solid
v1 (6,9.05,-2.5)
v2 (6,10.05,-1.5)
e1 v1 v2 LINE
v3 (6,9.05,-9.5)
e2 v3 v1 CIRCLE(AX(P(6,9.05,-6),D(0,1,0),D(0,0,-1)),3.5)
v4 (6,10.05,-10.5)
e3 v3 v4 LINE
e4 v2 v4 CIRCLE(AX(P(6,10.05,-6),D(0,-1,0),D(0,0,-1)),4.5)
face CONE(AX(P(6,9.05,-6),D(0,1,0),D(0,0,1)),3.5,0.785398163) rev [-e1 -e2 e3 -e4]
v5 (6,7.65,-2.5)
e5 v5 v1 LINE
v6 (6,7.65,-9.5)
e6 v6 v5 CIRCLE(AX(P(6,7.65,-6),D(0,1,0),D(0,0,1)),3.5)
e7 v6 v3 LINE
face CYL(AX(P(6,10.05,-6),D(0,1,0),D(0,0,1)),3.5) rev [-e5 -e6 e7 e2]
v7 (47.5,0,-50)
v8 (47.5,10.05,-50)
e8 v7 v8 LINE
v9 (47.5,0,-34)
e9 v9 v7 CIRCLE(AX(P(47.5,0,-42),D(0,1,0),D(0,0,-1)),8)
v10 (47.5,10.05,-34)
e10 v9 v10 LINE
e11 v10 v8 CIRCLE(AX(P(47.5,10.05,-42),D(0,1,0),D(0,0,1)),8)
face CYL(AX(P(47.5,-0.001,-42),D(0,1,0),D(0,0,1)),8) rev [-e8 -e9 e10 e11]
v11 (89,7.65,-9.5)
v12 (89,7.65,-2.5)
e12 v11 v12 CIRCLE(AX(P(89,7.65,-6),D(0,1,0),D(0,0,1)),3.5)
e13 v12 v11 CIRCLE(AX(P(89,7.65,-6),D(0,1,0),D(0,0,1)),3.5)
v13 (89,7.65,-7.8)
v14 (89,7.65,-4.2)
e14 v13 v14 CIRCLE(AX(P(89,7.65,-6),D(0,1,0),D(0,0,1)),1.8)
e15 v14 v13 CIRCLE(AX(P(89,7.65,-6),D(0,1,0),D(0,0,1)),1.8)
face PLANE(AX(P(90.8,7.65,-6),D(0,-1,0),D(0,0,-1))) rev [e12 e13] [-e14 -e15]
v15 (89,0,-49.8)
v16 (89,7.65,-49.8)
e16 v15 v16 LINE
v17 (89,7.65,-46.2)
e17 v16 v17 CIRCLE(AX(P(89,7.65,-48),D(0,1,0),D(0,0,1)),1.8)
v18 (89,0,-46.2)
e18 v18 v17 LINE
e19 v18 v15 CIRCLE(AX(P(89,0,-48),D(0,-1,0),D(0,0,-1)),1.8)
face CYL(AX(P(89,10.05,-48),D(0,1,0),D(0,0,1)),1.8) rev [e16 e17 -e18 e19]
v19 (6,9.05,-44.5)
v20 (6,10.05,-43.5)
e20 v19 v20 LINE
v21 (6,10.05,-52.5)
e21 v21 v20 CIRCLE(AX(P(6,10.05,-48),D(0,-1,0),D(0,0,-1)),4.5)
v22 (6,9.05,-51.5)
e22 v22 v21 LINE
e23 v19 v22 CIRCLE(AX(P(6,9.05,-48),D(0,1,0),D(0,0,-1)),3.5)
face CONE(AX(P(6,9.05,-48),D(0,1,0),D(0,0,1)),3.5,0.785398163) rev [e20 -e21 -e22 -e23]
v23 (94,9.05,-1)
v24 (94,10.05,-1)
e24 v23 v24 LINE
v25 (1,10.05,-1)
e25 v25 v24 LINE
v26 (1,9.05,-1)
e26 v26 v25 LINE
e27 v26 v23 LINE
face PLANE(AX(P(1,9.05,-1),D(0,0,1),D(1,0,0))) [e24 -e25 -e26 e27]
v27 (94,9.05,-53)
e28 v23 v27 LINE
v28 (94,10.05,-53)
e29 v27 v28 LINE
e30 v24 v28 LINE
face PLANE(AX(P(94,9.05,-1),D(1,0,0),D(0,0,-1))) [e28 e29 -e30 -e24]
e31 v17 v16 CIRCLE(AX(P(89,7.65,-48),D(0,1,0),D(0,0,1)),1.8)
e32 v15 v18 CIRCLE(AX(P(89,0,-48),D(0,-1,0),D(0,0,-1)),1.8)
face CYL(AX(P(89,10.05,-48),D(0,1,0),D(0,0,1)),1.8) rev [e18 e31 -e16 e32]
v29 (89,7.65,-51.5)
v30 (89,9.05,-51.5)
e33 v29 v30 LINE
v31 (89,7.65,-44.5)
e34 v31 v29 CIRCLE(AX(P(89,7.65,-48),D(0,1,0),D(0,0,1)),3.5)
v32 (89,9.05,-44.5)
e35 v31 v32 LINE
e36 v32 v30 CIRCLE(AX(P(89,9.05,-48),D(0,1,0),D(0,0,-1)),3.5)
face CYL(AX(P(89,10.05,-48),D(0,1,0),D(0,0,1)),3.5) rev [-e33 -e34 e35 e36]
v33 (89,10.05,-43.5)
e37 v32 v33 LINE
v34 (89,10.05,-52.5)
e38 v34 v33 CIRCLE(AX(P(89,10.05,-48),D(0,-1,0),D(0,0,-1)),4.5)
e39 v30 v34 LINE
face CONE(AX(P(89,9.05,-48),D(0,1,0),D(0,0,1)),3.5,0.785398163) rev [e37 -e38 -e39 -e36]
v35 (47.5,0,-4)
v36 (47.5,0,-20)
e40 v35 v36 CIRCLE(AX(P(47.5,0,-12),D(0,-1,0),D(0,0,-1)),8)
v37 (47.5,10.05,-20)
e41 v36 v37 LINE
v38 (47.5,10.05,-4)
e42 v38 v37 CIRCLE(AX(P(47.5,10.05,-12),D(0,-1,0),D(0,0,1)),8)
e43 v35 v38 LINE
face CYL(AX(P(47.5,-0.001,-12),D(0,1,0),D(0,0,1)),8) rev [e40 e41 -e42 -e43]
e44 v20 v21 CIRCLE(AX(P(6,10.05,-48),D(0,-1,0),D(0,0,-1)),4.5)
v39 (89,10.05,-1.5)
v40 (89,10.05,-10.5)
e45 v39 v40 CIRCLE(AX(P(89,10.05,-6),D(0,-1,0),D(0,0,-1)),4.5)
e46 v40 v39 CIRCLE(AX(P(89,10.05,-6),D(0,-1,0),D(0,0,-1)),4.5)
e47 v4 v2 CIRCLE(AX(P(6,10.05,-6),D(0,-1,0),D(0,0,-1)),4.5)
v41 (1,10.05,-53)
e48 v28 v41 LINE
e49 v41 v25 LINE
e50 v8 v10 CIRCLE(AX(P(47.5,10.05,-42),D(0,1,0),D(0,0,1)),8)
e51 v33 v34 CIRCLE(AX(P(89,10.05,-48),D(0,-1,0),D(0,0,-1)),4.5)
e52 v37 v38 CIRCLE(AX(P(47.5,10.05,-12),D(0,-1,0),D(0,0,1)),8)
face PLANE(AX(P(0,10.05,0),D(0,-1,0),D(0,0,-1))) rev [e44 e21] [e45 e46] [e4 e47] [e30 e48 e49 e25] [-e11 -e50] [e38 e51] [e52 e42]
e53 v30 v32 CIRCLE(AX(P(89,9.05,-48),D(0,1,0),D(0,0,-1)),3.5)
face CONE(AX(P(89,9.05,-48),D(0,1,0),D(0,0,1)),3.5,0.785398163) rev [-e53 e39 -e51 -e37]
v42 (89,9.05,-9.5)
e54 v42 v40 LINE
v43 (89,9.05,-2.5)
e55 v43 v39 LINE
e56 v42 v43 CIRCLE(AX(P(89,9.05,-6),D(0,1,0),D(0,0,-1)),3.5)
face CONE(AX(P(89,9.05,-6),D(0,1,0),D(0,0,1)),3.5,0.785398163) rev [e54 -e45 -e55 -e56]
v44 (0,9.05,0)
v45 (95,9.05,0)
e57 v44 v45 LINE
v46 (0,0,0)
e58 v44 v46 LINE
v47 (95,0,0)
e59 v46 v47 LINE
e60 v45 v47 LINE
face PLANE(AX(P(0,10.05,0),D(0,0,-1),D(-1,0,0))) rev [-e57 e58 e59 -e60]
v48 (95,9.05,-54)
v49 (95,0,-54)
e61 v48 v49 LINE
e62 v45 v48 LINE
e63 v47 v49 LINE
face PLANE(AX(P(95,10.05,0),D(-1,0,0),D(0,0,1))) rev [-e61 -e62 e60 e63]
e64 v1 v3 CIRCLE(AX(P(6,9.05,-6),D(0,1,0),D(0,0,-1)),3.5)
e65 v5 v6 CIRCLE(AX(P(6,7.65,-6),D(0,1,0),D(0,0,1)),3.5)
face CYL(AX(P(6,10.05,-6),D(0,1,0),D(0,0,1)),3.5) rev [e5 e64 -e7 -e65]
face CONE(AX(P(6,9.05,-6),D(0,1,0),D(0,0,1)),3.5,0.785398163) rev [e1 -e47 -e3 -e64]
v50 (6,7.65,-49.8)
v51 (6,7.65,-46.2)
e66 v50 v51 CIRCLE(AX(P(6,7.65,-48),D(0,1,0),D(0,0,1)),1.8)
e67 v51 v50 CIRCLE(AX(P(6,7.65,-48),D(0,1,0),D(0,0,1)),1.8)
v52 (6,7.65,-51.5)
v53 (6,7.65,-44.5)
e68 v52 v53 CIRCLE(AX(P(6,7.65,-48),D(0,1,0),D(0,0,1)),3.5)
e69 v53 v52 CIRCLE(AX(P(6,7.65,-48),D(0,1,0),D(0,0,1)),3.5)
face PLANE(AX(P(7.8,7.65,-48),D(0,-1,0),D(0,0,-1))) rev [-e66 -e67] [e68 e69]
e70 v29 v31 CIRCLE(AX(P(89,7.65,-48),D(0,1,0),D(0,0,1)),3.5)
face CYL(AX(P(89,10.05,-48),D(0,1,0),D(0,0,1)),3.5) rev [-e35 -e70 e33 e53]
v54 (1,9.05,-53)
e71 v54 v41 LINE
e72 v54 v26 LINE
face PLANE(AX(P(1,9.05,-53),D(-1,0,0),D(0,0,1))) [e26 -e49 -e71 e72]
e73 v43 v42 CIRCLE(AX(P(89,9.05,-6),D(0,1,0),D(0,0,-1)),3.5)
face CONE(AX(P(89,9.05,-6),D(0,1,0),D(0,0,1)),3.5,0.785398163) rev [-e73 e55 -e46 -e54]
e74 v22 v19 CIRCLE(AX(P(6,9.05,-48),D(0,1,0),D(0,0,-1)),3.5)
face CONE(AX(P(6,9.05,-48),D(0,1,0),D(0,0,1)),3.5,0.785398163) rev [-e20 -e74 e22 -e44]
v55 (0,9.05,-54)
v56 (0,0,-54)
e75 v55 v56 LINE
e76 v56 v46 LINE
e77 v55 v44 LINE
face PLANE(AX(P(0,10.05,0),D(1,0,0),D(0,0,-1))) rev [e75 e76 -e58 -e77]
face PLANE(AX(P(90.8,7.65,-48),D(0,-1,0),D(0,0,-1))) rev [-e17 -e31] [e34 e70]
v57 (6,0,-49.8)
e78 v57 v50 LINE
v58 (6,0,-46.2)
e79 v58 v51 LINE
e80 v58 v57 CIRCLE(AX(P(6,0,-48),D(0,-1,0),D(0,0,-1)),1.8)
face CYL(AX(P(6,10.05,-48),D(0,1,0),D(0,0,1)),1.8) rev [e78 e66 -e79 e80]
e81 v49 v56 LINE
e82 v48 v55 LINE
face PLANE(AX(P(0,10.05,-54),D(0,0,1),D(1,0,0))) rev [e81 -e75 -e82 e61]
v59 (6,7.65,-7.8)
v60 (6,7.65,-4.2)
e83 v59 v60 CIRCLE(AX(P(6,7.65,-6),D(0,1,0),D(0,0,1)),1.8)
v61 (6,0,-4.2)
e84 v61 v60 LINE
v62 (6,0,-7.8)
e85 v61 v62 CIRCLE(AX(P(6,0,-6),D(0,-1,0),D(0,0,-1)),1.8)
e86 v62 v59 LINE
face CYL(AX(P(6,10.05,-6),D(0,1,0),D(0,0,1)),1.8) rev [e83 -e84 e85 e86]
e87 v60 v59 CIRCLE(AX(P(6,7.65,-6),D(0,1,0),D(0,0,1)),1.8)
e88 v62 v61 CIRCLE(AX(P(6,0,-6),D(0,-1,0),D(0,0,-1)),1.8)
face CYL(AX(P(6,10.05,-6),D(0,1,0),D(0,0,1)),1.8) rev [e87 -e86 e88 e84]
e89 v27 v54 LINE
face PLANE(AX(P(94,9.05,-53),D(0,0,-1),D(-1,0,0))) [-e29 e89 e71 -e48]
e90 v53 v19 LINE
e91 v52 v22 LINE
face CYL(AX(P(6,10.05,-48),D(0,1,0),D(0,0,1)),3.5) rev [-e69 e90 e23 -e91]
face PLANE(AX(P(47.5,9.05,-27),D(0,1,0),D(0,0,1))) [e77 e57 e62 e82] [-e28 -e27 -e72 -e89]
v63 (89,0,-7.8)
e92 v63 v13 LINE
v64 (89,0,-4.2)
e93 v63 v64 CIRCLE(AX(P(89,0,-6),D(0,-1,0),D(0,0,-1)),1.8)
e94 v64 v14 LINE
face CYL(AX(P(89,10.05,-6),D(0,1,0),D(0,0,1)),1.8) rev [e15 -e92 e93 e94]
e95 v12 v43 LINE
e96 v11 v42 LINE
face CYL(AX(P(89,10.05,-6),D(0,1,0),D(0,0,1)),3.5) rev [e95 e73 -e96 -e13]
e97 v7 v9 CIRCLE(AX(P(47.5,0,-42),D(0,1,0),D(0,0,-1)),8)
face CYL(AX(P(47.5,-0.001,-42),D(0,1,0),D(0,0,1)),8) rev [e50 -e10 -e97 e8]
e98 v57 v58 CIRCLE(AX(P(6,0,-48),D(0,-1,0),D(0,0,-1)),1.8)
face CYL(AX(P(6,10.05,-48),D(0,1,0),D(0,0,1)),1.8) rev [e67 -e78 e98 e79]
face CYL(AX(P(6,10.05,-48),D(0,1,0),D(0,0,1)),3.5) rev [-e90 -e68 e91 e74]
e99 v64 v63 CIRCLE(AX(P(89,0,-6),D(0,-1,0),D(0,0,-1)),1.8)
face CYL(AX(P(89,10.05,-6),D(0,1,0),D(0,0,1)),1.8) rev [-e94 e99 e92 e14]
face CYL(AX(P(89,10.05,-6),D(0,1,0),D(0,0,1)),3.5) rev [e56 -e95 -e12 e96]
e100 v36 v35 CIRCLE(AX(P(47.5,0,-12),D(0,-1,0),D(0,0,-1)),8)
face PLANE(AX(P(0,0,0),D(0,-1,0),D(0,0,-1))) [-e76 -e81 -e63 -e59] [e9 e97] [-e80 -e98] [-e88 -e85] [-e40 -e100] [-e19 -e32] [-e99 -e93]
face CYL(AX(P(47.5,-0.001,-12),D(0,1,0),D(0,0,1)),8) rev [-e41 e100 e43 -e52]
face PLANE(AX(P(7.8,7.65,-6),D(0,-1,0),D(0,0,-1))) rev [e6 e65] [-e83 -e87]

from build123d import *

# Parameters (mm, degrees)
SKETCH1_W                                = 95
SKETCH1_H                                = 54
BOSS_EXTRUDE1_DEPTH                      = 10.05
SKETCH2_OUTSIDE_W                        = 118.948
SKETCH2_OUTSIDE_H                        = 77.948
SKETCH2_OUTSIDE_W_2                      = 93
SKETCH2_OUTSIDE_H_2                      = 52
CUT_EXTRUDE1_DEPTH                       = 1
CBORE_FOR_M3_PAN_HEAD_SCREW1_D           = 3.6
CBORE_FOR_M3_PAN_HEAD_SCREW1_CBORE_D     = 7
CBORE_FOR_M3_PAN_HEAD_SCREW1_CBORE_DEPTH = 2.4
CHAMFER1_SIZE                            = 1
CUT_EXTRUDE2_REACH                       = 111.736
SKETCH5_R                                = 8


with BuildPart() as part:
    # Sketch1 → Boss-Extrude1 (new body)
    with BuildSketch(Plane(origin=(0, 0, 0), x_dir=(1, 0, 0), z_dir=(0, 1, 0))):
        with Locations((47.5, 27)):
            Rectangle(SKETCH1_W, SKETCH1_H)
    extrude(amount=BOSS_EXTRUDE1_DEPTH)

    # Sketch2 outside → Cut-Extrude1 (cut)
    with BuildSketch(Plane(origin=(0, 10.05, 0), x_dir=(1, 0, 0), z_dir=(0, 1, 0))):
        with Locations((47.5, 27)):
            Rectangle(SKETCH2_OUTSIDE_W, SKETCH2_OUTSIDE_H)
        with Locations((47.5, 27)):
            Rectangle(SKETCH2_OUTSIDE_W_2, SKETCH2_OUTSIDE_H_2, mode=Mode.SUBTRACT)
    extrude(amount=-CUT_EXTRUDE1_DEPTH, mode=Mode.SUBTRACT)

    # CBORE for M3 Pan Head Screw1 (through all)
    with Locations(Plane(origin=(6, 10.05, -48), x_dir=(0, 0, 1), z_dir=(0, 1, 0))):
        with Locations((0, 0), (0, 83), (42, 83), (42, 0)):
            CounterBoreHole(CBORE_FOR_M3_PAN_HEAD_SCREW1_D / 2, CBORE_FOR_M3_PAN_HEAD_SCREW1_CBORE_D / 2, CBORE_FOR_M3_PAN_HEAD_SCREW1_CBORE_DEPTH)

    # Chamfer1
    chamfer1_edges = [part.edges().sort_by_distance(p)[0] for p in [
        (6, 10.05, -9.5),
        (89, 10.05, -9.5),
        (89, 10.05, -51.5),
        (6, 10.05, -51.5),
    ]]
    chamfer(chamfer1_edges, length=CHAMFER1_SIZE)

    # Sketch5 → Cut-Extrude2 (cut, up to next)
    with BuildSketch(Plane(origin=(0, 10.05, 0), x_dir=(1, 0, 0), z_dir=(0, 1, 0)), mode=Mode.PRIVATE) as cut_extrude2_sk1:
        with Locations(Location((47.5, 42, 0), (0, 0, 270))):
            Circle(SKETCH5_R)
    cut_extrude2_tool1 = extrude(cut_extrude2_sk1.sketch, amount=-CUT_EXTRUDE2_REACH, mode=Mode.PRIVATE) & part.part
    # Sketch5 → Cut-Extrude2 (cut, up to next)
    with BuildSketch(Plane(origin=(0, 10.05, 0), x_dir=(1, 0, 0), z_dir=(0, 1, 0)), mode=Mode.PRIVATE) as cut_extrude2_sk2:
        with Locations(Location((47.5, 12, 0), (0, 0, 270))):
            Circle(SKETCH5_R)
    cut_extrude2_tool2 = extrude(cut_extrude2_sk2.sketch, amount=-CUT_EXTRUDE2_REACH, mode=Mode.PRIVATE) & part.part
    add(cut_extrude2_tool1.solids().sort_by_distance((47.5, 10.05, -42))[0], mode=Mode.SUBTRACT)
    add(cut_extrude2_tool2.solids().sort_by_distance((47.5, 10.05, -12))[0], mode=Mode.SUBTRACT)


solid = part.part
